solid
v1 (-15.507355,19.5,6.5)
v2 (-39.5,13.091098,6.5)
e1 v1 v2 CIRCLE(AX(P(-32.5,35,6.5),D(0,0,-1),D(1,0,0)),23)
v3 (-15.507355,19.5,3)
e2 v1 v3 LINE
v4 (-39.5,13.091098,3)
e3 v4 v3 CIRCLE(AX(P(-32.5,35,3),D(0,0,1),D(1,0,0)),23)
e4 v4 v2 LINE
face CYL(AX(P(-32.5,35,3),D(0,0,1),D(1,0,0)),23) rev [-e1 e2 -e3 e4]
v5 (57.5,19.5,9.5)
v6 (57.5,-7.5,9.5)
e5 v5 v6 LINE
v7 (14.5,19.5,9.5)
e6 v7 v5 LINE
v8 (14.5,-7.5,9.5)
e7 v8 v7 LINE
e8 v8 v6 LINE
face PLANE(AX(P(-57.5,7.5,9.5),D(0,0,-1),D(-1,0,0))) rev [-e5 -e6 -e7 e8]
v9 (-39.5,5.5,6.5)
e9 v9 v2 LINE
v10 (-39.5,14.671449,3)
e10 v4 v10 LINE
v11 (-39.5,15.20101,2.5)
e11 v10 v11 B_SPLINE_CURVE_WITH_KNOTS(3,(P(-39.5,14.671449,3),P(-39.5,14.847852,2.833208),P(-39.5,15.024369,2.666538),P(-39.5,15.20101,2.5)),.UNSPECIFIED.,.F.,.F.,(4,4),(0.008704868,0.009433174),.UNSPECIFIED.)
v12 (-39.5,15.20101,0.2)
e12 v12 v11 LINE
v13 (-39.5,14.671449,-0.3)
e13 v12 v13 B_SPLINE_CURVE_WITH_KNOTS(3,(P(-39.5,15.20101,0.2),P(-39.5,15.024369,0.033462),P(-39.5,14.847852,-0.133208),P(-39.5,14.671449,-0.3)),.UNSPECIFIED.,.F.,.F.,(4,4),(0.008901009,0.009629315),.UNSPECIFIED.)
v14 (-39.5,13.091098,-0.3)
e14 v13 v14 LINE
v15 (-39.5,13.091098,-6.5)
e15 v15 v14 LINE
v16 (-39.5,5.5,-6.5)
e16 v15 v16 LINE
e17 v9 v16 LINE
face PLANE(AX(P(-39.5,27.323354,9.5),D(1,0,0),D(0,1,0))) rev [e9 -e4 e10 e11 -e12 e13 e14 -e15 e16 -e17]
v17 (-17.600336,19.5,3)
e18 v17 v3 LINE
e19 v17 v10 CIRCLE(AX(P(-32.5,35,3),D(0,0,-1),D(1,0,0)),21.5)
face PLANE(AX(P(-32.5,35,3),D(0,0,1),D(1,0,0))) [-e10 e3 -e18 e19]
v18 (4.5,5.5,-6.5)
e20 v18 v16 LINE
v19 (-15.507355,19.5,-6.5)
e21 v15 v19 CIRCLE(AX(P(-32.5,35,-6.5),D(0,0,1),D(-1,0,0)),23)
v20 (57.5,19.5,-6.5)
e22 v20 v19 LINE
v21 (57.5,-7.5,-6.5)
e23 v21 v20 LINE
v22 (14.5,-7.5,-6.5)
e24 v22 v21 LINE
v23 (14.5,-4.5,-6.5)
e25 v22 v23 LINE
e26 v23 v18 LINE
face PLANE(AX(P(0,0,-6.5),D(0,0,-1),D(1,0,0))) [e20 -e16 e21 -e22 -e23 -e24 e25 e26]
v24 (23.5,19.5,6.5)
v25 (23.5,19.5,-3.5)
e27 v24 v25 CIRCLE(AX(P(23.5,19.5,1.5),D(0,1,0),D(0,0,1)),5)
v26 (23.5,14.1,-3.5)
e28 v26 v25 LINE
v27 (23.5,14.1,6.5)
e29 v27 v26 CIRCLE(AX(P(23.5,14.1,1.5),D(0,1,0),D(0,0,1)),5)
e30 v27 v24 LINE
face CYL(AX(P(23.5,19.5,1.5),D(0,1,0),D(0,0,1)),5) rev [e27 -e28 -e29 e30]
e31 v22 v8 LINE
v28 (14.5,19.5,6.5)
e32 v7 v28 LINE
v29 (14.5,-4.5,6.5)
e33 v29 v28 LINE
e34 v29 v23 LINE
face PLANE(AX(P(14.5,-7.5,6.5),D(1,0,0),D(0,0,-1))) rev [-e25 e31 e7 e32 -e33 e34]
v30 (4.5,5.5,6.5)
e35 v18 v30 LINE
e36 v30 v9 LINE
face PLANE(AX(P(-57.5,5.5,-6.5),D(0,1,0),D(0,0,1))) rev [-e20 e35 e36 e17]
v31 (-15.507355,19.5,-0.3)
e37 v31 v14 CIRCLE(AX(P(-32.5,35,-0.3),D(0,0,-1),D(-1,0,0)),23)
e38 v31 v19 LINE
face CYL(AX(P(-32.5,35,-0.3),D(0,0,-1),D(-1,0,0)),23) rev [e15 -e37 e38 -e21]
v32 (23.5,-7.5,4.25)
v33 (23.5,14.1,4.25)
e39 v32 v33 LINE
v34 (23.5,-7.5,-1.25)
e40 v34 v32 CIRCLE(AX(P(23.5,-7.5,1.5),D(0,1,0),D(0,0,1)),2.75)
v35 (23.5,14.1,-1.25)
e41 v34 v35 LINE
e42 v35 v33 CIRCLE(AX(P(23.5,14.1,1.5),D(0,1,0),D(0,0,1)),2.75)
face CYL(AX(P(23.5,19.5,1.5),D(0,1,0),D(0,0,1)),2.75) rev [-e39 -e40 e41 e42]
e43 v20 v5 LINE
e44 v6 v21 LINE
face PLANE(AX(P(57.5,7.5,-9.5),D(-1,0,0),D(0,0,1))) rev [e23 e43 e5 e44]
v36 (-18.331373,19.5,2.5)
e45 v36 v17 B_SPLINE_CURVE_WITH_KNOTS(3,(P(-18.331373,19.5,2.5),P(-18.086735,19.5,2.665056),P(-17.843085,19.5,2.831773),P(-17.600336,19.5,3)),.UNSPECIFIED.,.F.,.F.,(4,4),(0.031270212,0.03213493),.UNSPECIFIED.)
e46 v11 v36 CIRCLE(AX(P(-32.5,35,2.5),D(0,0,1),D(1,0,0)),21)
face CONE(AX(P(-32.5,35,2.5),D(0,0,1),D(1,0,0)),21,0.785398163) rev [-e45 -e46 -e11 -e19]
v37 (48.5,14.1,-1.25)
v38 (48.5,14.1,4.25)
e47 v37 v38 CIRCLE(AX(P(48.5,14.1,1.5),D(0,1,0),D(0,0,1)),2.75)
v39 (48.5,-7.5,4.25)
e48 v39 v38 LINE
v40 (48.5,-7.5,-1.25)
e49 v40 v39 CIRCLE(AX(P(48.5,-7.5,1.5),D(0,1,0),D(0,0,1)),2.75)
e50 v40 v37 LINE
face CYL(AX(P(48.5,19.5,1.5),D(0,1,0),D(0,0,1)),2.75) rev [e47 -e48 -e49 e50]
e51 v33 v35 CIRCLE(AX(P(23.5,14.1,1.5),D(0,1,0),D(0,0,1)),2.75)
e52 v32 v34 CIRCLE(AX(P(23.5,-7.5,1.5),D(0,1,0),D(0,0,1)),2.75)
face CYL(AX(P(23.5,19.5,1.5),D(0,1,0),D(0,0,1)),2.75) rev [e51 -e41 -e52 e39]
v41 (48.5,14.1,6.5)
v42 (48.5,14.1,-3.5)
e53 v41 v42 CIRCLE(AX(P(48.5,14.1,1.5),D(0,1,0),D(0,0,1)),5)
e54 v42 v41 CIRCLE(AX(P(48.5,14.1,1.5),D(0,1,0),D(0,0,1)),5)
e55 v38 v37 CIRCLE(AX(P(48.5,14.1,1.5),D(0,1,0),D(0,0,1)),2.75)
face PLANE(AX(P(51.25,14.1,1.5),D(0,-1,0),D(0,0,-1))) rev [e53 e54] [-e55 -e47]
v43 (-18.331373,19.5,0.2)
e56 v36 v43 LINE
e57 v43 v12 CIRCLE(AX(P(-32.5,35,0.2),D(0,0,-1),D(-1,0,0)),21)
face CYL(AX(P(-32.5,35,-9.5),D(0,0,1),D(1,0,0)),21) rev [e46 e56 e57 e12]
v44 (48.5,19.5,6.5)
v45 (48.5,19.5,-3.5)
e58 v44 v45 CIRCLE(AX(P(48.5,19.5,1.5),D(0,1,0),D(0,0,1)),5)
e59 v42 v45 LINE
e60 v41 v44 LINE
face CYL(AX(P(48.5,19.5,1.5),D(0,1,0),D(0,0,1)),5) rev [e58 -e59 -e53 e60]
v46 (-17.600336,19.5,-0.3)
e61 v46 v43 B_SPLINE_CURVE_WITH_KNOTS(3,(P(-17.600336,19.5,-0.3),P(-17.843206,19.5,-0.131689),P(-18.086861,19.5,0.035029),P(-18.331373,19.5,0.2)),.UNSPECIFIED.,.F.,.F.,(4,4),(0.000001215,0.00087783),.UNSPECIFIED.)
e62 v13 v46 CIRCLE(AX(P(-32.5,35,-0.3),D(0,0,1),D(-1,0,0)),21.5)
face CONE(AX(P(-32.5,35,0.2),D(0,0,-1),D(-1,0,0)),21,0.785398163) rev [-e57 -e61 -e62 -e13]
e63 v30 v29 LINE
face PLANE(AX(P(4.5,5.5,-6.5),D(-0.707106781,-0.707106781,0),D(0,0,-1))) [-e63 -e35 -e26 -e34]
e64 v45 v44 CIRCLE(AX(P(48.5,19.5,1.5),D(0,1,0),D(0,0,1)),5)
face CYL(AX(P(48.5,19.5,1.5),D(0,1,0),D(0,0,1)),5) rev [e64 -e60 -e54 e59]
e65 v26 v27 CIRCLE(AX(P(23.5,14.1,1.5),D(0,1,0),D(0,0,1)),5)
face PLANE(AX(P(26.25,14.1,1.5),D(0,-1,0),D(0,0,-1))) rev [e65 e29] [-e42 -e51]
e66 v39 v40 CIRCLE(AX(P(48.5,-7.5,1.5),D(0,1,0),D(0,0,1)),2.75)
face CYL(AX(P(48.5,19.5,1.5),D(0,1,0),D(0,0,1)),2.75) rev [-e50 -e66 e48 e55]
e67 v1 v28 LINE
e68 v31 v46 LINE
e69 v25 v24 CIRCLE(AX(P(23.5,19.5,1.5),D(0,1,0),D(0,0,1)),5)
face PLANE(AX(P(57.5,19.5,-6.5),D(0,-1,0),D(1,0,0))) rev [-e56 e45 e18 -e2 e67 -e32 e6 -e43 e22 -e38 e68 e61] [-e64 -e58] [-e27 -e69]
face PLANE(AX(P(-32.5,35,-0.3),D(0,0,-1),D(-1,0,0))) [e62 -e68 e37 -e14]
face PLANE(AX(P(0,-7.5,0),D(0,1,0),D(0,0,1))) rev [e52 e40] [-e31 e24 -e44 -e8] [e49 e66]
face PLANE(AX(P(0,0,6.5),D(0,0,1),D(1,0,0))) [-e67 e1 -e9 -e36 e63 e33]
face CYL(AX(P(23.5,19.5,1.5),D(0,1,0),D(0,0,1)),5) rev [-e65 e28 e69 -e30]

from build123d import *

# Parameters (mm, degrees)
SKETCH_1_W                   = 115
SKETCH_1_H                   = 19
EXTRUDE_1_DEPTH              = 7.5
SKETCH_2_W                   = 72
SKETCH_2_H                   = 19
EXTRUDE_2_DEPTH              = 15
SKETCH_5_R                   = 23
CUT_EXTRUDE_3_DEPTH          = 6.5
CUT_EXTRUDE_START            = -9.2
SKETCH_6_R                   = 23
CUT_EXTRUDE_4_DEPTH          = 9.2
SKETCH_7_R                   = 21
CUT_EXTRUDE_5_DEPTH          = 63.998015842
FILLET_3_R                   = 2
CHAMFER_1_SIZE               = 0.5
SKETCH_8_W                   = 100
SKETCH_8_H                   = 30
CUT_EXTRUDE_8_DEPTH          = 3
SKETCH_12_W                  = 43
SKETCH_12_H                  = 3
CUT_EXTRUDE_9_DEPTH          = 61.178899957
SKETCH_13_W                  = 72
SKETCH_13_H                  = 13
CUT_EXTRUDE_10_DEPTH         = 64.099128362
SKETCH_14_W                  = 43
SKETCH_14_H                  = 15
EXTRUDE_3_DEPTH              = 16
SKETCH_16_W                  = 115
SKETCH_16_H                  = 3
CUT_EXTRUDE_14_DEPTH         = 64.784794426
CHAMFER_2_SIZE               = 10
HOLE_WIZARD_M5_1_D           = 5.5
HOLE_WIZARD_M5_1_CBORE_D     = 10
HOLE_WIZARD_M5_1_CBORE_DEPTH = 5.4
SKETCH_19_W                  = 25.462348227
SKETCH_19_H                  = 32.507755261
CUT_EXTRUDE_15_DEPTH         = 63.789330304


with BuildPart() as part:
    # 草图1 → 凸台-拉伸1 (new, symmetric)
    with BuildSketch(Plane(origin=(0, 0, 0), x_dir=(1, 0, 0), z_dir=(0, 1, 0))):
        Rectangle(SKETCH_1_W, SKETCH_1_H)
    extrude(amount=EXTRUDE_1_DEPTH, both=True)

    # 草图2 → 凸台-拉伸2 (add)
    with BuildSketch(Plane(origin=(0, 7.5, 0), x_dir=(1, 0, 0), z_dir=(0, 1, 0))):
        with Locations((-21.5, 0)):
            Rectangle(SKETCH_2_W, SKETCH_2_H)
    extrude(amount=EXTRUDE_2_DEPTH)

    # 草图5 → 切除-拉伸3 (cut)
    with BuildSketch(Plane.XY.offset(9.5)):
        with Locations((-32.5, 35)):
            Circle(SKETCH_5_R)
    extrude(amount=-CUT_EXTRUDE_3_DEPTH, mode=Mode.SUBTRACT)

    # 草图6 → 切除-拉伸4 (cut)
    with BuildSketch(Plane(origin=(0, 0, -9.5), x_dir=(-1, 0, 0), z_dir=(0, 0, -1)).offset(CUT_EXTRUDE_START)):
        with Locations((32.5, 35)):
            Circle(SKETCH_6_R)
    extrude(amount=CUT_EXTRUDE_4_DEPTH, mode=Mode.SUBTRACT)

    # 草图7 → 切除-拉伸5 (cut, through all)
    with BuildSketch(Plane.XY.offset(3)):
        with Locations((-32.5, 35)):
            Circle(SKETCH_7_R)
    extrude(amount=-CUT_EXTRUDE_5_DEPTH, mode=Mode.SUBTRACT)

    # 圆角3
    fillet_3_edges = [part.edges().sort_by_distance(p)[0] for p in [
        (-49.374537031, 22.5, 1.35),
        (-15.625462969, 22.5, 1.35),
    ]]
    fillet(fillet_3_edges, radius=FILLET_3_R)

    # 倒角1
    chamfer_1_edges = [part.edges().sort_by_distance(p)[0] for p in [
        (-51.080152824, 22.5, 3),
        (-13.919847176, 22.5, -0.3),
        (-32.5, 14, 3),
        (-32.5, 14, -0.3),
        (-51.080152824, 22.5, -0.3),
        (-49.493844118, 22.305787796, -0.3),
        (-15.506155882, 22.305787796, -0.3),
        (-13.919847176, 22.5, 3),
        (-49.493844118, 22.305787796, 3),
        (-15.506155882, 22.305787796, 3),
    ]]
    chamfer(chamfer_1_edges, length=CHAMFER_1_SIZE)

    # 草图8 → 切除-拉伸8 (cut)
    with BuildSketch(Plane.XY.offset(9.5)):
        with Locations((-35.5, 7.5)):
            Rectangle(SKETCH_8_W, SKETCH_8_H)
    cut_extrude_8 = extrude(amount=-CUT_EXTRUDE_8_DEPTH, mode=Mode.SUBTRACT)

    # 镜向1: 切除-拉伸8 across plane
    add(cut_extrude_8.mirror(Plane.XY), mode=Mode.SUBTRACT)

    # 草图12 → 切除-拉伸9 (cut, through all)
    with BuildSketch(Plane(origin=(0, 7.5, 0), x_dir=(1, 0, 0), z_dir=(0, 1, 0))):
        with Locations((36, 8)):
            Rectangle(SKETCH_12_W, SKETCH_12_H)
    extrude(amount=-CUT_EXTRUDE_9_DEPTH, mode=Mode.SUBTRACT)

    # 草图13 → 切除-拉伸10 (cut, through all)
    with BuildSketch(Plane.XY.offset(6.5)):
        with Locations((-21.5, -1)):
            Rectangle(SKETCH_13_W, SKETCH_13_H)
    extrude(amount=-CUT_EXTRUDE_10_DEPTH, mode=Mode.SUBTRACT)

    # 草图14 → 凸台-拉伸3 (add)
    with BuildSketch(Plane.XY.offset(9.5)):
        with Locations((36, 15)):
            Rectangle(SKETCH_14_W, SKETCH_14_H)
    extrude(amount=-EXTRUDE_3_DEPTH)

    # 草图16 → 切除-拉伸14 (cut, through all)
    with BuildSketch(Plane.XY.offset(9.5)):
        with Locations((0, 21)):
            Rectangle(SKETCH_16_W, SKETCH_16_H)
    extrude(amount=-CUT_EXTRUDE_14_DEPTH, mode=Mode.SUBTRACT)

    # 倒角2
    chamfer_2_edges = [part.edges().sort_by_distance(p)[0] for p in [
        (14.5, 5.5, 0),
    ]]
    chamfer(chamfer_2_edges, length=CHAMFER_2_SIZE)

    # M5 六角凹头螺钉的柱形沉头孔1 (through all)
    with Locations(Plane(origin=(0, 19.5, 0), x_dir=(1, 0, 0), z_dir=(0, 1, 0))):
        with Locations((23.5, -1.5), (48.5, -1.5)):
            CounterBoreHole(HOLE_WIZARD_M5_1_D / 2, HOLE_WIZARD_M5_1_CBORE_D / 2, HOLE_WIZARD_M5_1_CBORE_DEPTH)

    # 草图19 → 切除-拉伸15 (cut, through all)
    with BuildSketch(Plane(origin=(0, 0, -6.5), x_dir=(-1, 0, 0), z_dir=(0, 0, -1))):
        with Locations((52.231174114, 11.069476533)):
            Rectangle(SKETCH_19_W, SKETCH_19_H)
    extrude(amount=-CUT_EXTRUDE_15_DEPTH, mode=Mode.SUBTRACT)


solid = part.part
